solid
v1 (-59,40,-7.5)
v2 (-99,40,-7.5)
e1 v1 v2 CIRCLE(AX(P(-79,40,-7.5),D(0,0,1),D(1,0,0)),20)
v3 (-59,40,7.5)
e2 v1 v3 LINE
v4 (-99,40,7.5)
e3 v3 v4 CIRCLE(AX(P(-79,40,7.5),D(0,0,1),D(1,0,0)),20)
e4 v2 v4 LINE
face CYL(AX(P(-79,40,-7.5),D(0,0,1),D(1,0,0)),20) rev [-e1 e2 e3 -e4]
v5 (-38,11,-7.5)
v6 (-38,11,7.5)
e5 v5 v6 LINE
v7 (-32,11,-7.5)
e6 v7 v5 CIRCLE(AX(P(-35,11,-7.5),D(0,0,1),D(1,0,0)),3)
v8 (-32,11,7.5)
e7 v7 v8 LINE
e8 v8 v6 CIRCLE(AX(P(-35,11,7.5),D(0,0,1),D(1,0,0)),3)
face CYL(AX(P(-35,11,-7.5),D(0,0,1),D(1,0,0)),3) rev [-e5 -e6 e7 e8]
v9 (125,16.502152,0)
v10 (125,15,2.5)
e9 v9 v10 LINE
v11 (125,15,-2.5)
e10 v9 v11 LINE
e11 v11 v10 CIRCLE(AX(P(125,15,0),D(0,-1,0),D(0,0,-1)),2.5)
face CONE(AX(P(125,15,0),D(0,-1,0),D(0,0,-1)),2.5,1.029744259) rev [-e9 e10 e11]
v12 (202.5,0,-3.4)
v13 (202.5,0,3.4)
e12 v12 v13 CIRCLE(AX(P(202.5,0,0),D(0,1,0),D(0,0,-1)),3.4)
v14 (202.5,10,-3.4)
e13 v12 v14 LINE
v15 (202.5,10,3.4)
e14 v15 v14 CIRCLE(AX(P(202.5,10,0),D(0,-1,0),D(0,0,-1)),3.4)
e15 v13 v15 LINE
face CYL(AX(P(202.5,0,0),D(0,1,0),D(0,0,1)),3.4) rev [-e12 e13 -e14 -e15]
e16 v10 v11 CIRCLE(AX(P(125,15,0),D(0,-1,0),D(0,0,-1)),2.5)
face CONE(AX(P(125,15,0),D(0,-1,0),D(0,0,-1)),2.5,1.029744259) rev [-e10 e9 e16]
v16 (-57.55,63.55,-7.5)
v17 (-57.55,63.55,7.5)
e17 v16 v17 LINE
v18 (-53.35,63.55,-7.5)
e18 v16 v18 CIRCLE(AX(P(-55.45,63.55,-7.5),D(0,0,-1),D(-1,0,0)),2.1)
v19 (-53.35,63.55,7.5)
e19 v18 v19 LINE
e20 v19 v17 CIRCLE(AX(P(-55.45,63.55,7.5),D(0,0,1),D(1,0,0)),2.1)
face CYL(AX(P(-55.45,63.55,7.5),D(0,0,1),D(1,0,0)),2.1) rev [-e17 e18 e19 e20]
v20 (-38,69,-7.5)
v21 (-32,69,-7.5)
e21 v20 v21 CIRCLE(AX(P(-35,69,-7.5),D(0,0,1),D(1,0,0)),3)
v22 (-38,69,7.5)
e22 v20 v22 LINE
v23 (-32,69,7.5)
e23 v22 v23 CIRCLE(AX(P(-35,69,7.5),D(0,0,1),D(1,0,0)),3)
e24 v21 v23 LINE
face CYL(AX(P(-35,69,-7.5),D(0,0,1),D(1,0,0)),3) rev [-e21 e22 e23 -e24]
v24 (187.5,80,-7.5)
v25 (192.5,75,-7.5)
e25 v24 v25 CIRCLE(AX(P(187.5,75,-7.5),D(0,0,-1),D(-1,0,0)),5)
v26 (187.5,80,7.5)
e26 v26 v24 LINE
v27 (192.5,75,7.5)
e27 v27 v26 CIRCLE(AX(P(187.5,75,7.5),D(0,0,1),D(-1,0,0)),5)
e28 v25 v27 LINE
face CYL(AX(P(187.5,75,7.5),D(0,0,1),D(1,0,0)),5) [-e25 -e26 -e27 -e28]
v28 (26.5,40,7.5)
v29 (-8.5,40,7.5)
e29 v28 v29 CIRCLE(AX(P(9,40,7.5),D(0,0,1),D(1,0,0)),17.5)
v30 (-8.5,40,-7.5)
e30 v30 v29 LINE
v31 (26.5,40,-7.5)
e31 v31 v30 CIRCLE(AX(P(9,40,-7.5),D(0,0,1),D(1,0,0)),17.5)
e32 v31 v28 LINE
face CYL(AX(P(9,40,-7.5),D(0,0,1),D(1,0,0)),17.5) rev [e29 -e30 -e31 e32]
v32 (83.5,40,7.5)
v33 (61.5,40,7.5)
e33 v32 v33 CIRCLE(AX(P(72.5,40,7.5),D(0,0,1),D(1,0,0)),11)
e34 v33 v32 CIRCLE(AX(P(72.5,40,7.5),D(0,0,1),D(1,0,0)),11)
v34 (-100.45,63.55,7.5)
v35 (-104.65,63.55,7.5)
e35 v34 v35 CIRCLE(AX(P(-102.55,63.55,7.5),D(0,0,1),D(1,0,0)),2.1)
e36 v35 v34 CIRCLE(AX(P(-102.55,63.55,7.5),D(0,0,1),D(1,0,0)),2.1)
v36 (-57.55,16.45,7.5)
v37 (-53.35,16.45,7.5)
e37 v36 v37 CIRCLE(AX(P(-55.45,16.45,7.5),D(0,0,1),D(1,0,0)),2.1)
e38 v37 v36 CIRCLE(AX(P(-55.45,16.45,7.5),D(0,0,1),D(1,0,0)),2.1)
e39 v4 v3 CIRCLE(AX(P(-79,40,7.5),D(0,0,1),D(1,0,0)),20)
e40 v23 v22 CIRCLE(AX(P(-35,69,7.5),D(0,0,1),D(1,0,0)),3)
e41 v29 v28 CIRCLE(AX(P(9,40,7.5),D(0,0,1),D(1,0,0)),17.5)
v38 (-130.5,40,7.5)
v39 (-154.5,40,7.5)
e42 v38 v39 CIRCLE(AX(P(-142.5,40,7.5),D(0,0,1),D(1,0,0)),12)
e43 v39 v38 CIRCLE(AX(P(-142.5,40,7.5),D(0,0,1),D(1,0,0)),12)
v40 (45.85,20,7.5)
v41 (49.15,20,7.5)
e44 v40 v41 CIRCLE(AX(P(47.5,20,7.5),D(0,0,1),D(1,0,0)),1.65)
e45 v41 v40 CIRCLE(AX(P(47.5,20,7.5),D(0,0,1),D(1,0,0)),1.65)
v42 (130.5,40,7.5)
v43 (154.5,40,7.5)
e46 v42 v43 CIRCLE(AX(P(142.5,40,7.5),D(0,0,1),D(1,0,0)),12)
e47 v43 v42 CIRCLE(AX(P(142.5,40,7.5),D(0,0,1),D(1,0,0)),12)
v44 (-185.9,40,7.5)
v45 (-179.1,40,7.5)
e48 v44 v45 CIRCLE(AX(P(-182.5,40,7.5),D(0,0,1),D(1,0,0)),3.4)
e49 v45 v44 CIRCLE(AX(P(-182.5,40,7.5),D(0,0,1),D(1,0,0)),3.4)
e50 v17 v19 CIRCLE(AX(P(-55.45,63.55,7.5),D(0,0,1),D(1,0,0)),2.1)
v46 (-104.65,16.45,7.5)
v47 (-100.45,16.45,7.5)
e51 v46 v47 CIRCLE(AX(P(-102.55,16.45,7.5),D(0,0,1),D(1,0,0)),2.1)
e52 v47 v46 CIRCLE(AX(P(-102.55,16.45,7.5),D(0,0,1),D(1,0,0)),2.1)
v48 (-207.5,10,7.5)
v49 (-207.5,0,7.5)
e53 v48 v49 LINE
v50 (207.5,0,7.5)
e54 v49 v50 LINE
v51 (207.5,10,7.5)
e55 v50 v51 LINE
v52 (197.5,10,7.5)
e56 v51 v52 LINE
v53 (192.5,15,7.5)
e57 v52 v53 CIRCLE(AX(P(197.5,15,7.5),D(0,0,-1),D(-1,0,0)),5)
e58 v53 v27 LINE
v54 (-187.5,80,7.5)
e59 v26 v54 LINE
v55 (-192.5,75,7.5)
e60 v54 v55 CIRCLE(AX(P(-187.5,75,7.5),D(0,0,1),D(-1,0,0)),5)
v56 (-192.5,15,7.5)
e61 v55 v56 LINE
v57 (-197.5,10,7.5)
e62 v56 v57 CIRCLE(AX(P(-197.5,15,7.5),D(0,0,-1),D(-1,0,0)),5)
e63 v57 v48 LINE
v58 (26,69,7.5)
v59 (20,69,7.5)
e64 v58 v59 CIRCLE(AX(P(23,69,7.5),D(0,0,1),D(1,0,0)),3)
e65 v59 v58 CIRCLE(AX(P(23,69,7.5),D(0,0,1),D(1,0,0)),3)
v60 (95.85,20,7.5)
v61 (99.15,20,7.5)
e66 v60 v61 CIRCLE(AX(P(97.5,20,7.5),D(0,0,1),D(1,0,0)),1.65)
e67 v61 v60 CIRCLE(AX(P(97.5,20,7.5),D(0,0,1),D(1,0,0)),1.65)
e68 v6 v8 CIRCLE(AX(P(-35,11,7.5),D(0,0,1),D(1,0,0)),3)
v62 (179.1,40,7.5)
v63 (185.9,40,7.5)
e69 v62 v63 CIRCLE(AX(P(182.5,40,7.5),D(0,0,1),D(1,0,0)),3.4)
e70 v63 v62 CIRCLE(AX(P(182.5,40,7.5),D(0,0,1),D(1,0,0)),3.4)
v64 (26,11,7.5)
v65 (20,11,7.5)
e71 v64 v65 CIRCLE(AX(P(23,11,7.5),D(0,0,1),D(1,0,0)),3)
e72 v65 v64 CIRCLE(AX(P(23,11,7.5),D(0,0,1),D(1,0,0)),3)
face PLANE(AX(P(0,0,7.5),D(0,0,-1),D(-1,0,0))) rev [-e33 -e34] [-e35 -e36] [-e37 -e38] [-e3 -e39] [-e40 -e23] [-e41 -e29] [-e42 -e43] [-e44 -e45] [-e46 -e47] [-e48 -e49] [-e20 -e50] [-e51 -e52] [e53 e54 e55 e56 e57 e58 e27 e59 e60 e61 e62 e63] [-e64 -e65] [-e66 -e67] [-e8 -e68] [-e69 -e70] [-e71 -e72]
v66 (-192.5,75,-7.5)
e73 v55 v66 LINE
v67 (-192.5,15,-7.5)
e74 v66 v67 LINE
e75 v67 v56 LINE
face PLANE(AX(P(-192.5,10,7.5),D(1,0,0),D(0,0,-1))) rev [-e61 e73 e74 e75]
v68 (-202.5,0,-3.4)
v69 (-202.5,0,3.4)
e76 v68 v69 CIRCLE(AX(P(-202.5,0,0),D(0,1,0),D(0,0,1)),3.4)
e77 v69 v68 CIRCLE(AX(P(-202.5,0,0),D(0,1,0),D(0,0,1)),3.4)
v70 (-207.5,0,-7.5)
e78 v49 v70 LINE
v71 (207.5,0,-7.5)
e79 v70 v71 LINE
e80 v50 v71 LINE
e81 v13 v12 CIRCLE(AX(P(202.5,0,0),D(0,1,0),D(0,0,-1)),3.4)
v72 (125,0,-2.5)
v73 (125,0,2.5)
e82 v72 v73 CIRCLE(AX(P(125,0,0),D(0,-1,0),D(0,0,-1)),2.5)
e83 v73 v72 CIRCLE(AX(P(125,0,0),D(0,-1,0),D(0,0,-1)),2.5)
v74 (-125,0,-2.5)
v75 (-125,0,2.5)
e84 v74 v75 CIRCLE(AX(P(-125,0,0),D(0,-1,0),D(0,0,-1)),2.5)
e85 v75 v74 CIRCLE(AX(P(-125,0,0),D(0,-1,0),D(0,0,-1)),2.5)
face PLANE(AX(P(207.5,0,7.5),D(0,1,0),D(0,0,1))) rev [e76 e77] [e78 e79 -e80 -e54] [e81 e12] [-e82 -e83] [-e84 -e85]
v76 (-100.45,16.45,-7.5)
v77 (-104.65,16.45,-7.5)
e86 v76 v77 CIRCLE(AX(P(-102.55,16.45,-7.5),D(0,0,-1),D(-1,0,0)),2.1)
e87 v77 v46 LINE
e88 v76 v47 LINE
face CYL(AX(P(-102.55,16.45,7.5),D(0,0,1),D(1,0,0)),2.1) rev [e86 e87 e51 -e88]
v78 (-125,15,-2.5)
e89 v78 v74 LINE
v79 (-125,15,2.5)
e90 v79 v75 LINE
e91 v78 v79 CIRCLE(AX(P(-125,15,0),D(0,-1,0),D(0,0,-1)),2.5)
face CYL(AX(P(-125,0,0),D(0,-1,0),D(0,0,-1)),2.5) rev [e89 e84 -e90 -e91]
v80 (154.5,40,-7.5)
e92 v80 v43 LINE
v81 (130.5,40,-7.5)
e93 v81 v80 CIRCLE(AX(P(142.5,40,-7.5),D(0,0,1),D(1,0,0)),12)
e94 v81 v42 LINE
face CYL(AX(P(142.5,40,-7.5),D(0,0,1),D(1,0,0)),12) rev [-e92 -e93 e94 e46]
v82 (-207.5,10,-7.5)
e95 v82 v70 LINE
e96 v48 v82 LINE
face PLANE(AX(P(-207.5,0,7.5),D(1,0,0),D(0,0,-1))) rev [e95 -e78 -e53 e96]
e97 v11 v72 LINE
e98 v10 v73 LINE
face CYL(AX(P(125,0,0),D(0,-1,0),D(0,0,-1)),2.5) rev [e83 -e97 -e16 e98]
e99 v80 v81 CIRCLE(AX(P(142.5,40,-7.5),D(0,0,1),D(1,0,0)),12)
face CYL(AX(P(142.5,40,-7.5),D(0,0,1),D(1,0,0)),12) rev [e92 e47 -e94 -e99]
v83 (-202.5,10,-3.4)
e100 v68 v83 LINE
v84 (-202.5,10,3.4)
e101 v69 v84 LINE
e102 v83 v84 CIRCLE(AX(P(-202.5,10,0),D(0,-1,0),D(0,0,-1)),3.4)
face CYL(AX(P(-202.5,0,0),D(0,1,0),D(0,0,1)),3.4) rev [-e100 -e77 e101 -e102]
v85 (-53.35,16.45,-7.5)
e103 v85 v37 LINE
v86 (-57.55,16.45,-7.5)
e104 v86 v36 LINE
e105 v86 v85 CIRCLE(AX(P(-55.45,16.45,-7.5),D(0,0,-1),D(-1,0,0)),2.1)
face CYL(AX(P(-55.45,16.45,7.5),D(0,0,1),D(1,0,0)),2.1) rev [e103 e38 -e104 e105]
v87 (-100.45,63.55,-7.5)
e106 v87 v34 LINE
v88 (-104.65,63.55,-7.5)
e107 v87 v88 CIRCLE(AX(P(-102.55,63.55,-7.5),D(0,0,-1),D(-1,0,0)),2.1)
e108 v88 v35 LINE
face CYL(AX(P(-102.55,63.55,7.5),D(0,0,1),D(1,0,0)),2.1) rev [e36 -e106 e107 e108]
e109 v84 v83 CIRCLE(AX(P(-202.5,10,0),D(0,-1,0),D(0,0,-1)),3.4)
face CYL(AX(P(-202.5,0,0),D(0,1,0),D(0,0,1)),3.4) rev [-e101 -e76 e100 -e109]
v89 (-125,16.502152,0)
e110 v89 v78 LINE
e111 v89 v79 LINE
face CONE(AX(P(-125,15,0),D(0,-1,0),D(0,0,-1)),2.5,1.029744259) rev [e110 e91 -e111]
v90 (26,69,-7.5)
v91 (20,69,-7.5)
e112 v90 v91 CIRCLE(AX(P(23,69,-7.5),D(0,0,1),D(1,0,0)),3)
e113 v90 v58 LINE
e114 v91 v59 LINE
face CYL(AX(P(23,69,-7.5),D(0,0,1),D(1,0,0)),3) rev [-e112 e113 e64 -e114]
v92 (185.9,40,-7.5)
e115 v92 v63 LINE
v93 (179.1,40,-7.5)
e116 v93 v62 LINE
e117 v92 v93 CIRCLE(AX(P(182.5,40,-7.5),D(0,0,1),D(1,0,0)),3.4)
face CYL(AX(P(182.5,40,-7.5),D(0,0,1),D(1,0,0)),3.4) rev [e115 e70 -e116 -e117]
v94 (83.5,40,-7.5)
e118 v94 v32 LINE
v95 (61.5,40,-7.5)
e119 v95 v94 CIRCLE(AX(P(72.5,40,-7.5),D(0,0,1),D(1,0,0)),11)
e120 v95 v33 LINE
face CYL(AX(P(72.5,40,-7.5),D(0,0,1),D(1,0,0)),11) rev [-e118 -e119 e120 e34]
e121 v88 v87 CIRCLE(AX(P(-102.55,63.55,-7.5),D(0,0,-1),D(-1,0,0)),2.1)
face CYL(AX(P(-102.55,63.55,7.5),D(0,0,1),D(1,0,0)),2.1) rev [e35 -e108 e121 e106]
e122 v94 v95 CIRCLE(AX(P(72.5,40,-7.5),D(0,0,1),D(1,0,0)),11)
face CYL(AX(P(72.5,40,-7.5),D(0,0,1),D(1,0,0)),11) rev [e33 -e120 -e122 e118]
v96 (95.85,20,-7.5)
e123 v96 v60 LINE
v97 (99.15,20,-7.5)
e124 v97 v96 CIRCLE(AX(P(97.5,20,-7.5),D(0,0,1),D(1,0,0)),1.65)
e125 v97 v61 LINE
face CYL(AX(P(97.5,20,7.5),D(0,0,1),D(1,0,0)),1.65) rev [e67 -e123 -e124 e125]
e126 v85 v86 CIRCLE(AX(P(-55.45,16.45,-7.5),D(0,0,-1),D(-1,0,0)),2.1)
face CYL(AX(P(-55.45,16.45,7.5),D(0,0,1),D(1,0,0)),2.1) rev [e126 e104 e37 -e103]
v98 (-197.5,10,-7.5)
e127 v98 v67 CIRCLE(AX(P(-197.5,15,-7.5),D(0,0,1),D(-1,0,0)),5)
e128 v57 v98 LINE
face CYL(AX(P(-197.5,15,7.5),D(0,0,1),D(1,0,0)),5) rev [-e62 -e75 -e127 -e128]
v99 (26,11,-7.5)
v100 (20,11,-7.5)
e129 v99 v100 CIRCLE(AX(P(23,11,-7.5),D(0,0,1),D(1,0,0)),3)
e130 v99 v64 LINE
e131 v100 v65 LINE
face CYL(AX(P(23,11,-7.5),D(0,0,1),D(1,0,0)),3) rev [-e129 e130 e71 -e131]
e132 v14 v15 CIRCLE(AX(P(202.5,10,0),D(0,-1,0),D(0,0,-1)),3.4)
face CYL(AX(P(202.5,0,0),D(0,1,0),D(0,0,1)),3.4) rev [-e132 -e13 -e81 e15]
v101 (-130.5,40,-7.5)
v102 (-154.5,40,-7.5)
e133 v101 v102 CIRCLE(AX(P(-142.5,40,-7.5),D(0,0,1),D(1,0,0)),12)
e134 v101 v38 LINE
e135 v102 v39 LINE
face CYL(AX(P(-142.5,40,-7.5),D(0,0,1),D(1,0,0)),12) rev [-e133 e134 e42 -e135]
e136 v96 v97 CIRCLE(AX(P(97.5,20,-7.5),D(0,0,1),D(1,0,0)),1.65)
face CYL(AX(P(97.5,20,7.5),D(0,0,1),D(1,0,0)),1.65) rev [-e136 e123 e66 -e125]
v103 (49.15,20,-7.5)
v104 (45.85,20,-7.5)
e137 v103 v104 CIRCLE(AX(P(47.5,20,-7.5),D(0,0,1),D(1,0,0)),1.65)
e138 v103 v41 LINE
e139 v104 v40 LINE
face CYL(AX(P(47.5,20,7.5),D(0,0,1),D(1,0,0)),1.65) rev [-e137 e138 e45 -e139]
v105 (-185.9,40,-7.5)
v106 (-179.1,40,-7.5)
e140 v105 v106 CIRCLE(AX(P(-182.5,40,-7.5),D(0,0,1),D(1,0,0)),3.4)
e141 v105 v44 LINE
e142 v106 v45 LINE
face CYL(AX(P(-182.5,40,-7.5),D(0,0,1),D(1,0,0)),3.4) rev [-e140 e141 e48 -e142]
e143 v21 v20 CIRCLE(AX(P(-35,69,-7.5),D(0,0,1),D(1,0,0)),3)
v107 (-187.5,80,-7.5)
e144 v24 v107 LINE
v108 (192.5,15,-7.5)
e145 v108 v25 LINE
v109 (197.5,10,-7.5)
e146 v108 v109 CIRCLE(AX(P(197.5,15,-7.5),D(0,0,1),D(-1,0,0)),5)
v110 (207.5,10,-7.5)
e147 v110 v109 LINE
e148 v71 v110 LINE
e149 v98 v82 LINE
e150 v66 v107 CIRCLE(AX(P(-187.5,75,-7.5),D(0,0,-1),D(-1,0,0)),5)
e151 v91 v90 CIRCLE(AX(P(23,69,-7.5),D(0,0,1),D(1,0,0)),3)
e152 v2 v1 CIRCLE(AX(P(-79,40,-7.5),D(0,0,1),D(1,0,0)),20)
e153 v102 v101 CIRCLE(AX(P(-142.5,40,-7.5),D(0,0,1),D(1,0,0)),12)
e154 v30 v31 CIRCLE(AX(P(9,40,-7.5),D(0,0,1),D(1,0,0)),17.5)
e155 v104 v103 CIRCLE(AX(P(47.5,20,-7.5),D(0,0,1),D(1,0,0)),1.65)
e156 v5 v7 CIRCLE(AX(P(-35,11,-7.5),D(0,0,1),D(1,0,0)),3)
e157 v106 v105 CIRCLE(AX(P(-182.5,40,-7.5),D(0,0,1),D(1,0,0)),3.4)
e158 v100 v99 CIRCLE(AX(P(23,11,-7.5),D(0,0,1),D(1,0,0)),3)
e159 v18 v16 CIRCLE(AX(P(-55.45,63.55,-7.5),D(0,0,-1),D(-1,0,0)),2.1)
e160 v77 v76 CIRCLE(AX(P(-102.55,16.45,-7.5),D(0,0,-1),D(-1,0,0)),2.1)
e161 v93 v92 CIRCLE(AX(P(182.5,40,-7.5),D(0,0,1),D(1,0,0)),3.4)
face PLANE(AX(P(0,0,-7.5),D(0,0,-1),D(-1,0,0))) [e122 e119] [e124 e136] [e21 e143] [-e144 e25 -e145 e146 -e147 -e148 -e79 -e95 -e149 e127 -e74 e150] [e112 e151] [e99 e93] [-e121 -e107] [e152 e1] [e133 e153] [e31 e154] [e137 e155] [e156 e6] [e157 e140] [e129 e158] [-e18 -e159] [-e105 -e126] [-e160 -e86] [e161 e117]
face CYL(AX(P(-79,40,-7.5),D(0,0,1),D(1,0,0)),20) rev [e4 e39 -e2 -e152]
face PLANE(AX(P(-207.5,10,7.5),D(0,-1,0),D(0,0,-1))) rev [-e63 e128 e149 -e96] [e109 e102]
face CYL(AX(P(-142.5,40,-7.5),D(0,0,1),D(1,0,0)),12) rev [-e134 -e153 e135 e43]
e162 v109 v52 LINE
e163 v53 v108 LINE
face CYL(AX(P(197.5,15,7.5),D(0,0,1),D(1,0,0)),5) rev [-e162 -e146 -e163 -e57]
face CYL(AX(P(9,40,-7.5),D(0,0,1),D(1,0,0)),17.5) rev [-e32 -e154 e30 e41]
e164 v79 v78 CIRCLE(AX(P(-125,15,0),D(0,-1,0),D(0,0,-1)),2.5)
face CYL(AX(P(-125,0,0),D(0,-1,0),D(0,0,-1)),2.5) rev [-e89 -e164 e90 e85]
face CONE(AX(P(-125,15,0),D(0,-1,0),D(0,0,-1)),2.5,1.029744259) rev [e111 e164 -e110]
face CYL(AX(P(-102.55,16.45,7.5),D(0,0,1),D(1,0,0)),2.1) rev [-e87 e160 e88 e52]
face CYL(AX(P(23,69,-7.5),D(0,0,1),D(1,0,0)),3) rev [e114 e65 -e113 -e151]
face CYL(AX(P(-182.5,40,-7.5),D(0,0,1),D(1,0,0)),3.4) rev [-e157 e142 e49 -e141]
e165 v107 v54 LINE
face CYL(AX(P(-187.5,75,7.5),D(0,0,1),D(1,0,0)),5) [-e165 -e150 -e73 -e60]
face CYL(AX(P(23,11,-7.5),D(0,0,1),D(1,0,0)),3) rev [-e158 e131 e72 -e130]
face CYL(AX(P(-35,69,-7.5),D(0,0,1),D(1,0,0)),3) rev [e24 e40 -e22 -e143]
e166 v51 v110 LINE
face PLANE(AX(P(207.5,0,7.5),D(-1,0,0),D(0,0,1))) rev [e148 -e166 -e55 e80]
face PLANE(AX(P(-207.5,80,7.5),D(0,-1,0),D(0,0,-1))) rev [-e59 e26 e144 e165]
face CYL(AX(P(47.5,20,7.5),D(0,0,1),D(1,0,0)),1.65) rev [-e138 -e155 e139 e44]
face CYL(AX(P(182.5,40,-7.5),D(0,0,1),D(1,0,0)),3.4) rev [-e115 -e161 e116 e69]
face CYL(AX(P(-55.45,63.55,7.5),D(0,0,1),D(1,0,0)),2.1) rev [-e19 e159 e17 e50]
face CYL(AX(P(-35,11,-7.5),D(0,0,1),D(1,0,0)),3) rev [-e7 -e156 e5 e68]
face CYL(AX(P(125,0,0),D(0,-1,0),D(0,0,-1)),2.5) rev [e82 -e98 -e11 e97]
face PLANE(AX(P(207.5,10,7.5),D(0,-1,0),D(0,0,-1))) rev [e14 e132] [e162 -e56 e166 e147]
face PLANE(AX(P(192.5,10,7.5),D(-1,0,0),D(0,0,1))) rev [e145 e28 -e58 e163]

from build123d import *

# Parameters (mm, degrees)
BOSS_EXTRUDE1_DEPTH   = 7.5
SKETCH2_R             = 12
SKETCH2_R_2           = 17.5
SKETCH2_R_3           = 11
SKETCH2_R_4           = 20
SKETCH2_R_5           = 3.4
CUT_EXTRUDE1_DEPTH    = 15
SKETCH3_R             = 3
CUT_EXTRUDE2_DEPTH    = 15
SKETCH4_R             = 3.4
CUT_EXTRUDE3_DEPTH    = 223.514044501
FILLET1_R             = 5
M4_TAPPED_HOLE1_D     = 3.3
M5_TAPPED_HOLE1_D     = 4.2
SKETCH10_W            = 15
SKETCH10_H            = 40
CUT_EXTRUDE4_DEPTH    = 223.892911507
FILLET2_R             = 5
M6_TAPPED_HOLE1_D     = 5
M6_TAPPED_HOLE1_DEPTH = 15
M6_TAPPED_HOLE1_TIP   = 1.502151548


with BuildPart() as part:
    # Sketch1 → Boss-Extrude1 (new, symmetric)
    with BuildSketch(Plane.XY):
        Polygon((207.5, 0), (-207.5, 0), (-207.5, 10), (-192.5, 10), (-192.5, 70), (-207.5, 70), (-207.5, 80), (207.5, 80), (207.5, 70), (192.5, 70), (192.5, 10), (207.5, 10), align=None)
    extrude(amount=BOSS_EXTRUDE1_DEPTH, both=True)

    # Sketch2 → Cut-Extrude1 (cut)
    with BuildSketch(Plane.XY.offset(7.5)):
        with Locations((-142.5, 40)):
            Circle(SKETCH2_R)
        with Locations((9, 40)):
            Circle(SKETCH2_R_2)
        with Locations((72.5, 40)):
            Circle(SKETCH2_R_3)
        with Locations((-79, 40)):
            Circle(SKETCH2_R_4)
        with Locations((142.5, 40)):
            Circle(SKETCH2_R)
        with Locations((-182.5, 40)):
            Circle(SKETCH2_R_5)
        with Locations((182.5, 40)):
            Circle(SKETCH2_R_5)
    extrude(amount=-CUT_EXTRUDE1_DEPTH, mode=Mode.SUBTRACT)

    # Sketch3 → Cut-Extrude2 (cut)
    with BuildSketch(Plane.XY.offset(7.5)):
        with Locations((-35, 69)):
            Circle(SKETCH3_R)
        with Locations((23, 69)):
            Circle(SKETCH3_R)
        with Locations((23, 11)):
            Circle(SKETCH3_R)
        with Locations((-35, 11)):
            Circle(SKETCH3_R)
    extrude(amount=-CUT_EXTRUDE2_DEPTH, mode=Mode.SUBTRACT)

    # Sketch4 → Cut-Extrude3 (cut, through all)
    with BuildSketch(Plane(origin=(0, 80, 0), x_dir=(1, 0, 0), z_dir=(0, 1, 0))):
        with Locations(Location((-202.5, 0, 0), (0, 0, 270))):
            Circle(SKETCH4_R)
        with Locations(Location((202.5, 0, 0), (0, 0, 180))):
            Circle(SKETCH4_R)
    extrude(amount=-CUT_EXTRUDE3_DEPTH, mode=Mode.SUBTRACT)

    # Fillet1
    fillet1_edges = [part.edges().sort_by_distance(p)[0] for p in [
        (-192.5, 10, 0),
        (-192.5, 70, 0),
        (192.5, 70, 0),
        (192.5, 10, 0),
    ]]
    fillet(fillet1_edges, radius=FILLET1_R)

    # M4 Tapped Hole1 (through all)
    with Locations(Plane.XY.offset(7.5)):
        with Locations((47.5, 20), (97.5, 20)):
            Hole(M4_TAPPED_HOLE1_D / 2)

    # M5 Tapped Hole1 (through all)
    with Locations(Plane.XY.offset(7.5)):
        with Locations((-102.55, 63.55), (-55.45, 16.45), (-102.55, 16.45), (-55.45, 63.55)):
            Hole(M5_TAPPED_HOLE1_D / 2)

    # Sketch10 → Cut-Extrude4 (cut, through all)
    with BuildSketch(Plane.XY.offset(7.5)):
        with Locations((-200, 60)):
            Rectangle(SKETCH10_W, SKETCH10_H)
        with Locations((200, 60)):
            Rectangle(SKETCH10_W, SKETCH10_H)
    extrude(amount=-CUT_EXTRUDE4_DEPTH, mode=Mode.SUBTRACT)

    # Fillet2
    fillet2_edges = [part.edges().sort_by_distance(p)[0] for p in [
        (-192.5, 80, 0),
        (192.5, 80, 0),
    ]]
    fillet(fillet2_edges, radius=FILLET2_R)

    # M6 Tapped Hole1
    with Locations(Plane(origin=(0, 0, 0), x_dir=(-1, 0, 0), z_dir=(0, -1, 0))):
        with Locations((-125, 0), (125, 0)):
            Hole(M6_TAPPED_HOLE1_D / 2, depth=M6_TAPPED_HOLE1_DEPTH)
            with Locations((0, 0, -(M6_TAPPED_HOLE1_DEPTH + M6_TAPPED_HOLE1_TIP / 2))):  # 118° drill point
                Cone(0, M6_TAPPED_HOLE1_D / 2, M6_TAPPED_HOLE1_TIP, mode=Mode.SUBTRACT)


solid = part.part
